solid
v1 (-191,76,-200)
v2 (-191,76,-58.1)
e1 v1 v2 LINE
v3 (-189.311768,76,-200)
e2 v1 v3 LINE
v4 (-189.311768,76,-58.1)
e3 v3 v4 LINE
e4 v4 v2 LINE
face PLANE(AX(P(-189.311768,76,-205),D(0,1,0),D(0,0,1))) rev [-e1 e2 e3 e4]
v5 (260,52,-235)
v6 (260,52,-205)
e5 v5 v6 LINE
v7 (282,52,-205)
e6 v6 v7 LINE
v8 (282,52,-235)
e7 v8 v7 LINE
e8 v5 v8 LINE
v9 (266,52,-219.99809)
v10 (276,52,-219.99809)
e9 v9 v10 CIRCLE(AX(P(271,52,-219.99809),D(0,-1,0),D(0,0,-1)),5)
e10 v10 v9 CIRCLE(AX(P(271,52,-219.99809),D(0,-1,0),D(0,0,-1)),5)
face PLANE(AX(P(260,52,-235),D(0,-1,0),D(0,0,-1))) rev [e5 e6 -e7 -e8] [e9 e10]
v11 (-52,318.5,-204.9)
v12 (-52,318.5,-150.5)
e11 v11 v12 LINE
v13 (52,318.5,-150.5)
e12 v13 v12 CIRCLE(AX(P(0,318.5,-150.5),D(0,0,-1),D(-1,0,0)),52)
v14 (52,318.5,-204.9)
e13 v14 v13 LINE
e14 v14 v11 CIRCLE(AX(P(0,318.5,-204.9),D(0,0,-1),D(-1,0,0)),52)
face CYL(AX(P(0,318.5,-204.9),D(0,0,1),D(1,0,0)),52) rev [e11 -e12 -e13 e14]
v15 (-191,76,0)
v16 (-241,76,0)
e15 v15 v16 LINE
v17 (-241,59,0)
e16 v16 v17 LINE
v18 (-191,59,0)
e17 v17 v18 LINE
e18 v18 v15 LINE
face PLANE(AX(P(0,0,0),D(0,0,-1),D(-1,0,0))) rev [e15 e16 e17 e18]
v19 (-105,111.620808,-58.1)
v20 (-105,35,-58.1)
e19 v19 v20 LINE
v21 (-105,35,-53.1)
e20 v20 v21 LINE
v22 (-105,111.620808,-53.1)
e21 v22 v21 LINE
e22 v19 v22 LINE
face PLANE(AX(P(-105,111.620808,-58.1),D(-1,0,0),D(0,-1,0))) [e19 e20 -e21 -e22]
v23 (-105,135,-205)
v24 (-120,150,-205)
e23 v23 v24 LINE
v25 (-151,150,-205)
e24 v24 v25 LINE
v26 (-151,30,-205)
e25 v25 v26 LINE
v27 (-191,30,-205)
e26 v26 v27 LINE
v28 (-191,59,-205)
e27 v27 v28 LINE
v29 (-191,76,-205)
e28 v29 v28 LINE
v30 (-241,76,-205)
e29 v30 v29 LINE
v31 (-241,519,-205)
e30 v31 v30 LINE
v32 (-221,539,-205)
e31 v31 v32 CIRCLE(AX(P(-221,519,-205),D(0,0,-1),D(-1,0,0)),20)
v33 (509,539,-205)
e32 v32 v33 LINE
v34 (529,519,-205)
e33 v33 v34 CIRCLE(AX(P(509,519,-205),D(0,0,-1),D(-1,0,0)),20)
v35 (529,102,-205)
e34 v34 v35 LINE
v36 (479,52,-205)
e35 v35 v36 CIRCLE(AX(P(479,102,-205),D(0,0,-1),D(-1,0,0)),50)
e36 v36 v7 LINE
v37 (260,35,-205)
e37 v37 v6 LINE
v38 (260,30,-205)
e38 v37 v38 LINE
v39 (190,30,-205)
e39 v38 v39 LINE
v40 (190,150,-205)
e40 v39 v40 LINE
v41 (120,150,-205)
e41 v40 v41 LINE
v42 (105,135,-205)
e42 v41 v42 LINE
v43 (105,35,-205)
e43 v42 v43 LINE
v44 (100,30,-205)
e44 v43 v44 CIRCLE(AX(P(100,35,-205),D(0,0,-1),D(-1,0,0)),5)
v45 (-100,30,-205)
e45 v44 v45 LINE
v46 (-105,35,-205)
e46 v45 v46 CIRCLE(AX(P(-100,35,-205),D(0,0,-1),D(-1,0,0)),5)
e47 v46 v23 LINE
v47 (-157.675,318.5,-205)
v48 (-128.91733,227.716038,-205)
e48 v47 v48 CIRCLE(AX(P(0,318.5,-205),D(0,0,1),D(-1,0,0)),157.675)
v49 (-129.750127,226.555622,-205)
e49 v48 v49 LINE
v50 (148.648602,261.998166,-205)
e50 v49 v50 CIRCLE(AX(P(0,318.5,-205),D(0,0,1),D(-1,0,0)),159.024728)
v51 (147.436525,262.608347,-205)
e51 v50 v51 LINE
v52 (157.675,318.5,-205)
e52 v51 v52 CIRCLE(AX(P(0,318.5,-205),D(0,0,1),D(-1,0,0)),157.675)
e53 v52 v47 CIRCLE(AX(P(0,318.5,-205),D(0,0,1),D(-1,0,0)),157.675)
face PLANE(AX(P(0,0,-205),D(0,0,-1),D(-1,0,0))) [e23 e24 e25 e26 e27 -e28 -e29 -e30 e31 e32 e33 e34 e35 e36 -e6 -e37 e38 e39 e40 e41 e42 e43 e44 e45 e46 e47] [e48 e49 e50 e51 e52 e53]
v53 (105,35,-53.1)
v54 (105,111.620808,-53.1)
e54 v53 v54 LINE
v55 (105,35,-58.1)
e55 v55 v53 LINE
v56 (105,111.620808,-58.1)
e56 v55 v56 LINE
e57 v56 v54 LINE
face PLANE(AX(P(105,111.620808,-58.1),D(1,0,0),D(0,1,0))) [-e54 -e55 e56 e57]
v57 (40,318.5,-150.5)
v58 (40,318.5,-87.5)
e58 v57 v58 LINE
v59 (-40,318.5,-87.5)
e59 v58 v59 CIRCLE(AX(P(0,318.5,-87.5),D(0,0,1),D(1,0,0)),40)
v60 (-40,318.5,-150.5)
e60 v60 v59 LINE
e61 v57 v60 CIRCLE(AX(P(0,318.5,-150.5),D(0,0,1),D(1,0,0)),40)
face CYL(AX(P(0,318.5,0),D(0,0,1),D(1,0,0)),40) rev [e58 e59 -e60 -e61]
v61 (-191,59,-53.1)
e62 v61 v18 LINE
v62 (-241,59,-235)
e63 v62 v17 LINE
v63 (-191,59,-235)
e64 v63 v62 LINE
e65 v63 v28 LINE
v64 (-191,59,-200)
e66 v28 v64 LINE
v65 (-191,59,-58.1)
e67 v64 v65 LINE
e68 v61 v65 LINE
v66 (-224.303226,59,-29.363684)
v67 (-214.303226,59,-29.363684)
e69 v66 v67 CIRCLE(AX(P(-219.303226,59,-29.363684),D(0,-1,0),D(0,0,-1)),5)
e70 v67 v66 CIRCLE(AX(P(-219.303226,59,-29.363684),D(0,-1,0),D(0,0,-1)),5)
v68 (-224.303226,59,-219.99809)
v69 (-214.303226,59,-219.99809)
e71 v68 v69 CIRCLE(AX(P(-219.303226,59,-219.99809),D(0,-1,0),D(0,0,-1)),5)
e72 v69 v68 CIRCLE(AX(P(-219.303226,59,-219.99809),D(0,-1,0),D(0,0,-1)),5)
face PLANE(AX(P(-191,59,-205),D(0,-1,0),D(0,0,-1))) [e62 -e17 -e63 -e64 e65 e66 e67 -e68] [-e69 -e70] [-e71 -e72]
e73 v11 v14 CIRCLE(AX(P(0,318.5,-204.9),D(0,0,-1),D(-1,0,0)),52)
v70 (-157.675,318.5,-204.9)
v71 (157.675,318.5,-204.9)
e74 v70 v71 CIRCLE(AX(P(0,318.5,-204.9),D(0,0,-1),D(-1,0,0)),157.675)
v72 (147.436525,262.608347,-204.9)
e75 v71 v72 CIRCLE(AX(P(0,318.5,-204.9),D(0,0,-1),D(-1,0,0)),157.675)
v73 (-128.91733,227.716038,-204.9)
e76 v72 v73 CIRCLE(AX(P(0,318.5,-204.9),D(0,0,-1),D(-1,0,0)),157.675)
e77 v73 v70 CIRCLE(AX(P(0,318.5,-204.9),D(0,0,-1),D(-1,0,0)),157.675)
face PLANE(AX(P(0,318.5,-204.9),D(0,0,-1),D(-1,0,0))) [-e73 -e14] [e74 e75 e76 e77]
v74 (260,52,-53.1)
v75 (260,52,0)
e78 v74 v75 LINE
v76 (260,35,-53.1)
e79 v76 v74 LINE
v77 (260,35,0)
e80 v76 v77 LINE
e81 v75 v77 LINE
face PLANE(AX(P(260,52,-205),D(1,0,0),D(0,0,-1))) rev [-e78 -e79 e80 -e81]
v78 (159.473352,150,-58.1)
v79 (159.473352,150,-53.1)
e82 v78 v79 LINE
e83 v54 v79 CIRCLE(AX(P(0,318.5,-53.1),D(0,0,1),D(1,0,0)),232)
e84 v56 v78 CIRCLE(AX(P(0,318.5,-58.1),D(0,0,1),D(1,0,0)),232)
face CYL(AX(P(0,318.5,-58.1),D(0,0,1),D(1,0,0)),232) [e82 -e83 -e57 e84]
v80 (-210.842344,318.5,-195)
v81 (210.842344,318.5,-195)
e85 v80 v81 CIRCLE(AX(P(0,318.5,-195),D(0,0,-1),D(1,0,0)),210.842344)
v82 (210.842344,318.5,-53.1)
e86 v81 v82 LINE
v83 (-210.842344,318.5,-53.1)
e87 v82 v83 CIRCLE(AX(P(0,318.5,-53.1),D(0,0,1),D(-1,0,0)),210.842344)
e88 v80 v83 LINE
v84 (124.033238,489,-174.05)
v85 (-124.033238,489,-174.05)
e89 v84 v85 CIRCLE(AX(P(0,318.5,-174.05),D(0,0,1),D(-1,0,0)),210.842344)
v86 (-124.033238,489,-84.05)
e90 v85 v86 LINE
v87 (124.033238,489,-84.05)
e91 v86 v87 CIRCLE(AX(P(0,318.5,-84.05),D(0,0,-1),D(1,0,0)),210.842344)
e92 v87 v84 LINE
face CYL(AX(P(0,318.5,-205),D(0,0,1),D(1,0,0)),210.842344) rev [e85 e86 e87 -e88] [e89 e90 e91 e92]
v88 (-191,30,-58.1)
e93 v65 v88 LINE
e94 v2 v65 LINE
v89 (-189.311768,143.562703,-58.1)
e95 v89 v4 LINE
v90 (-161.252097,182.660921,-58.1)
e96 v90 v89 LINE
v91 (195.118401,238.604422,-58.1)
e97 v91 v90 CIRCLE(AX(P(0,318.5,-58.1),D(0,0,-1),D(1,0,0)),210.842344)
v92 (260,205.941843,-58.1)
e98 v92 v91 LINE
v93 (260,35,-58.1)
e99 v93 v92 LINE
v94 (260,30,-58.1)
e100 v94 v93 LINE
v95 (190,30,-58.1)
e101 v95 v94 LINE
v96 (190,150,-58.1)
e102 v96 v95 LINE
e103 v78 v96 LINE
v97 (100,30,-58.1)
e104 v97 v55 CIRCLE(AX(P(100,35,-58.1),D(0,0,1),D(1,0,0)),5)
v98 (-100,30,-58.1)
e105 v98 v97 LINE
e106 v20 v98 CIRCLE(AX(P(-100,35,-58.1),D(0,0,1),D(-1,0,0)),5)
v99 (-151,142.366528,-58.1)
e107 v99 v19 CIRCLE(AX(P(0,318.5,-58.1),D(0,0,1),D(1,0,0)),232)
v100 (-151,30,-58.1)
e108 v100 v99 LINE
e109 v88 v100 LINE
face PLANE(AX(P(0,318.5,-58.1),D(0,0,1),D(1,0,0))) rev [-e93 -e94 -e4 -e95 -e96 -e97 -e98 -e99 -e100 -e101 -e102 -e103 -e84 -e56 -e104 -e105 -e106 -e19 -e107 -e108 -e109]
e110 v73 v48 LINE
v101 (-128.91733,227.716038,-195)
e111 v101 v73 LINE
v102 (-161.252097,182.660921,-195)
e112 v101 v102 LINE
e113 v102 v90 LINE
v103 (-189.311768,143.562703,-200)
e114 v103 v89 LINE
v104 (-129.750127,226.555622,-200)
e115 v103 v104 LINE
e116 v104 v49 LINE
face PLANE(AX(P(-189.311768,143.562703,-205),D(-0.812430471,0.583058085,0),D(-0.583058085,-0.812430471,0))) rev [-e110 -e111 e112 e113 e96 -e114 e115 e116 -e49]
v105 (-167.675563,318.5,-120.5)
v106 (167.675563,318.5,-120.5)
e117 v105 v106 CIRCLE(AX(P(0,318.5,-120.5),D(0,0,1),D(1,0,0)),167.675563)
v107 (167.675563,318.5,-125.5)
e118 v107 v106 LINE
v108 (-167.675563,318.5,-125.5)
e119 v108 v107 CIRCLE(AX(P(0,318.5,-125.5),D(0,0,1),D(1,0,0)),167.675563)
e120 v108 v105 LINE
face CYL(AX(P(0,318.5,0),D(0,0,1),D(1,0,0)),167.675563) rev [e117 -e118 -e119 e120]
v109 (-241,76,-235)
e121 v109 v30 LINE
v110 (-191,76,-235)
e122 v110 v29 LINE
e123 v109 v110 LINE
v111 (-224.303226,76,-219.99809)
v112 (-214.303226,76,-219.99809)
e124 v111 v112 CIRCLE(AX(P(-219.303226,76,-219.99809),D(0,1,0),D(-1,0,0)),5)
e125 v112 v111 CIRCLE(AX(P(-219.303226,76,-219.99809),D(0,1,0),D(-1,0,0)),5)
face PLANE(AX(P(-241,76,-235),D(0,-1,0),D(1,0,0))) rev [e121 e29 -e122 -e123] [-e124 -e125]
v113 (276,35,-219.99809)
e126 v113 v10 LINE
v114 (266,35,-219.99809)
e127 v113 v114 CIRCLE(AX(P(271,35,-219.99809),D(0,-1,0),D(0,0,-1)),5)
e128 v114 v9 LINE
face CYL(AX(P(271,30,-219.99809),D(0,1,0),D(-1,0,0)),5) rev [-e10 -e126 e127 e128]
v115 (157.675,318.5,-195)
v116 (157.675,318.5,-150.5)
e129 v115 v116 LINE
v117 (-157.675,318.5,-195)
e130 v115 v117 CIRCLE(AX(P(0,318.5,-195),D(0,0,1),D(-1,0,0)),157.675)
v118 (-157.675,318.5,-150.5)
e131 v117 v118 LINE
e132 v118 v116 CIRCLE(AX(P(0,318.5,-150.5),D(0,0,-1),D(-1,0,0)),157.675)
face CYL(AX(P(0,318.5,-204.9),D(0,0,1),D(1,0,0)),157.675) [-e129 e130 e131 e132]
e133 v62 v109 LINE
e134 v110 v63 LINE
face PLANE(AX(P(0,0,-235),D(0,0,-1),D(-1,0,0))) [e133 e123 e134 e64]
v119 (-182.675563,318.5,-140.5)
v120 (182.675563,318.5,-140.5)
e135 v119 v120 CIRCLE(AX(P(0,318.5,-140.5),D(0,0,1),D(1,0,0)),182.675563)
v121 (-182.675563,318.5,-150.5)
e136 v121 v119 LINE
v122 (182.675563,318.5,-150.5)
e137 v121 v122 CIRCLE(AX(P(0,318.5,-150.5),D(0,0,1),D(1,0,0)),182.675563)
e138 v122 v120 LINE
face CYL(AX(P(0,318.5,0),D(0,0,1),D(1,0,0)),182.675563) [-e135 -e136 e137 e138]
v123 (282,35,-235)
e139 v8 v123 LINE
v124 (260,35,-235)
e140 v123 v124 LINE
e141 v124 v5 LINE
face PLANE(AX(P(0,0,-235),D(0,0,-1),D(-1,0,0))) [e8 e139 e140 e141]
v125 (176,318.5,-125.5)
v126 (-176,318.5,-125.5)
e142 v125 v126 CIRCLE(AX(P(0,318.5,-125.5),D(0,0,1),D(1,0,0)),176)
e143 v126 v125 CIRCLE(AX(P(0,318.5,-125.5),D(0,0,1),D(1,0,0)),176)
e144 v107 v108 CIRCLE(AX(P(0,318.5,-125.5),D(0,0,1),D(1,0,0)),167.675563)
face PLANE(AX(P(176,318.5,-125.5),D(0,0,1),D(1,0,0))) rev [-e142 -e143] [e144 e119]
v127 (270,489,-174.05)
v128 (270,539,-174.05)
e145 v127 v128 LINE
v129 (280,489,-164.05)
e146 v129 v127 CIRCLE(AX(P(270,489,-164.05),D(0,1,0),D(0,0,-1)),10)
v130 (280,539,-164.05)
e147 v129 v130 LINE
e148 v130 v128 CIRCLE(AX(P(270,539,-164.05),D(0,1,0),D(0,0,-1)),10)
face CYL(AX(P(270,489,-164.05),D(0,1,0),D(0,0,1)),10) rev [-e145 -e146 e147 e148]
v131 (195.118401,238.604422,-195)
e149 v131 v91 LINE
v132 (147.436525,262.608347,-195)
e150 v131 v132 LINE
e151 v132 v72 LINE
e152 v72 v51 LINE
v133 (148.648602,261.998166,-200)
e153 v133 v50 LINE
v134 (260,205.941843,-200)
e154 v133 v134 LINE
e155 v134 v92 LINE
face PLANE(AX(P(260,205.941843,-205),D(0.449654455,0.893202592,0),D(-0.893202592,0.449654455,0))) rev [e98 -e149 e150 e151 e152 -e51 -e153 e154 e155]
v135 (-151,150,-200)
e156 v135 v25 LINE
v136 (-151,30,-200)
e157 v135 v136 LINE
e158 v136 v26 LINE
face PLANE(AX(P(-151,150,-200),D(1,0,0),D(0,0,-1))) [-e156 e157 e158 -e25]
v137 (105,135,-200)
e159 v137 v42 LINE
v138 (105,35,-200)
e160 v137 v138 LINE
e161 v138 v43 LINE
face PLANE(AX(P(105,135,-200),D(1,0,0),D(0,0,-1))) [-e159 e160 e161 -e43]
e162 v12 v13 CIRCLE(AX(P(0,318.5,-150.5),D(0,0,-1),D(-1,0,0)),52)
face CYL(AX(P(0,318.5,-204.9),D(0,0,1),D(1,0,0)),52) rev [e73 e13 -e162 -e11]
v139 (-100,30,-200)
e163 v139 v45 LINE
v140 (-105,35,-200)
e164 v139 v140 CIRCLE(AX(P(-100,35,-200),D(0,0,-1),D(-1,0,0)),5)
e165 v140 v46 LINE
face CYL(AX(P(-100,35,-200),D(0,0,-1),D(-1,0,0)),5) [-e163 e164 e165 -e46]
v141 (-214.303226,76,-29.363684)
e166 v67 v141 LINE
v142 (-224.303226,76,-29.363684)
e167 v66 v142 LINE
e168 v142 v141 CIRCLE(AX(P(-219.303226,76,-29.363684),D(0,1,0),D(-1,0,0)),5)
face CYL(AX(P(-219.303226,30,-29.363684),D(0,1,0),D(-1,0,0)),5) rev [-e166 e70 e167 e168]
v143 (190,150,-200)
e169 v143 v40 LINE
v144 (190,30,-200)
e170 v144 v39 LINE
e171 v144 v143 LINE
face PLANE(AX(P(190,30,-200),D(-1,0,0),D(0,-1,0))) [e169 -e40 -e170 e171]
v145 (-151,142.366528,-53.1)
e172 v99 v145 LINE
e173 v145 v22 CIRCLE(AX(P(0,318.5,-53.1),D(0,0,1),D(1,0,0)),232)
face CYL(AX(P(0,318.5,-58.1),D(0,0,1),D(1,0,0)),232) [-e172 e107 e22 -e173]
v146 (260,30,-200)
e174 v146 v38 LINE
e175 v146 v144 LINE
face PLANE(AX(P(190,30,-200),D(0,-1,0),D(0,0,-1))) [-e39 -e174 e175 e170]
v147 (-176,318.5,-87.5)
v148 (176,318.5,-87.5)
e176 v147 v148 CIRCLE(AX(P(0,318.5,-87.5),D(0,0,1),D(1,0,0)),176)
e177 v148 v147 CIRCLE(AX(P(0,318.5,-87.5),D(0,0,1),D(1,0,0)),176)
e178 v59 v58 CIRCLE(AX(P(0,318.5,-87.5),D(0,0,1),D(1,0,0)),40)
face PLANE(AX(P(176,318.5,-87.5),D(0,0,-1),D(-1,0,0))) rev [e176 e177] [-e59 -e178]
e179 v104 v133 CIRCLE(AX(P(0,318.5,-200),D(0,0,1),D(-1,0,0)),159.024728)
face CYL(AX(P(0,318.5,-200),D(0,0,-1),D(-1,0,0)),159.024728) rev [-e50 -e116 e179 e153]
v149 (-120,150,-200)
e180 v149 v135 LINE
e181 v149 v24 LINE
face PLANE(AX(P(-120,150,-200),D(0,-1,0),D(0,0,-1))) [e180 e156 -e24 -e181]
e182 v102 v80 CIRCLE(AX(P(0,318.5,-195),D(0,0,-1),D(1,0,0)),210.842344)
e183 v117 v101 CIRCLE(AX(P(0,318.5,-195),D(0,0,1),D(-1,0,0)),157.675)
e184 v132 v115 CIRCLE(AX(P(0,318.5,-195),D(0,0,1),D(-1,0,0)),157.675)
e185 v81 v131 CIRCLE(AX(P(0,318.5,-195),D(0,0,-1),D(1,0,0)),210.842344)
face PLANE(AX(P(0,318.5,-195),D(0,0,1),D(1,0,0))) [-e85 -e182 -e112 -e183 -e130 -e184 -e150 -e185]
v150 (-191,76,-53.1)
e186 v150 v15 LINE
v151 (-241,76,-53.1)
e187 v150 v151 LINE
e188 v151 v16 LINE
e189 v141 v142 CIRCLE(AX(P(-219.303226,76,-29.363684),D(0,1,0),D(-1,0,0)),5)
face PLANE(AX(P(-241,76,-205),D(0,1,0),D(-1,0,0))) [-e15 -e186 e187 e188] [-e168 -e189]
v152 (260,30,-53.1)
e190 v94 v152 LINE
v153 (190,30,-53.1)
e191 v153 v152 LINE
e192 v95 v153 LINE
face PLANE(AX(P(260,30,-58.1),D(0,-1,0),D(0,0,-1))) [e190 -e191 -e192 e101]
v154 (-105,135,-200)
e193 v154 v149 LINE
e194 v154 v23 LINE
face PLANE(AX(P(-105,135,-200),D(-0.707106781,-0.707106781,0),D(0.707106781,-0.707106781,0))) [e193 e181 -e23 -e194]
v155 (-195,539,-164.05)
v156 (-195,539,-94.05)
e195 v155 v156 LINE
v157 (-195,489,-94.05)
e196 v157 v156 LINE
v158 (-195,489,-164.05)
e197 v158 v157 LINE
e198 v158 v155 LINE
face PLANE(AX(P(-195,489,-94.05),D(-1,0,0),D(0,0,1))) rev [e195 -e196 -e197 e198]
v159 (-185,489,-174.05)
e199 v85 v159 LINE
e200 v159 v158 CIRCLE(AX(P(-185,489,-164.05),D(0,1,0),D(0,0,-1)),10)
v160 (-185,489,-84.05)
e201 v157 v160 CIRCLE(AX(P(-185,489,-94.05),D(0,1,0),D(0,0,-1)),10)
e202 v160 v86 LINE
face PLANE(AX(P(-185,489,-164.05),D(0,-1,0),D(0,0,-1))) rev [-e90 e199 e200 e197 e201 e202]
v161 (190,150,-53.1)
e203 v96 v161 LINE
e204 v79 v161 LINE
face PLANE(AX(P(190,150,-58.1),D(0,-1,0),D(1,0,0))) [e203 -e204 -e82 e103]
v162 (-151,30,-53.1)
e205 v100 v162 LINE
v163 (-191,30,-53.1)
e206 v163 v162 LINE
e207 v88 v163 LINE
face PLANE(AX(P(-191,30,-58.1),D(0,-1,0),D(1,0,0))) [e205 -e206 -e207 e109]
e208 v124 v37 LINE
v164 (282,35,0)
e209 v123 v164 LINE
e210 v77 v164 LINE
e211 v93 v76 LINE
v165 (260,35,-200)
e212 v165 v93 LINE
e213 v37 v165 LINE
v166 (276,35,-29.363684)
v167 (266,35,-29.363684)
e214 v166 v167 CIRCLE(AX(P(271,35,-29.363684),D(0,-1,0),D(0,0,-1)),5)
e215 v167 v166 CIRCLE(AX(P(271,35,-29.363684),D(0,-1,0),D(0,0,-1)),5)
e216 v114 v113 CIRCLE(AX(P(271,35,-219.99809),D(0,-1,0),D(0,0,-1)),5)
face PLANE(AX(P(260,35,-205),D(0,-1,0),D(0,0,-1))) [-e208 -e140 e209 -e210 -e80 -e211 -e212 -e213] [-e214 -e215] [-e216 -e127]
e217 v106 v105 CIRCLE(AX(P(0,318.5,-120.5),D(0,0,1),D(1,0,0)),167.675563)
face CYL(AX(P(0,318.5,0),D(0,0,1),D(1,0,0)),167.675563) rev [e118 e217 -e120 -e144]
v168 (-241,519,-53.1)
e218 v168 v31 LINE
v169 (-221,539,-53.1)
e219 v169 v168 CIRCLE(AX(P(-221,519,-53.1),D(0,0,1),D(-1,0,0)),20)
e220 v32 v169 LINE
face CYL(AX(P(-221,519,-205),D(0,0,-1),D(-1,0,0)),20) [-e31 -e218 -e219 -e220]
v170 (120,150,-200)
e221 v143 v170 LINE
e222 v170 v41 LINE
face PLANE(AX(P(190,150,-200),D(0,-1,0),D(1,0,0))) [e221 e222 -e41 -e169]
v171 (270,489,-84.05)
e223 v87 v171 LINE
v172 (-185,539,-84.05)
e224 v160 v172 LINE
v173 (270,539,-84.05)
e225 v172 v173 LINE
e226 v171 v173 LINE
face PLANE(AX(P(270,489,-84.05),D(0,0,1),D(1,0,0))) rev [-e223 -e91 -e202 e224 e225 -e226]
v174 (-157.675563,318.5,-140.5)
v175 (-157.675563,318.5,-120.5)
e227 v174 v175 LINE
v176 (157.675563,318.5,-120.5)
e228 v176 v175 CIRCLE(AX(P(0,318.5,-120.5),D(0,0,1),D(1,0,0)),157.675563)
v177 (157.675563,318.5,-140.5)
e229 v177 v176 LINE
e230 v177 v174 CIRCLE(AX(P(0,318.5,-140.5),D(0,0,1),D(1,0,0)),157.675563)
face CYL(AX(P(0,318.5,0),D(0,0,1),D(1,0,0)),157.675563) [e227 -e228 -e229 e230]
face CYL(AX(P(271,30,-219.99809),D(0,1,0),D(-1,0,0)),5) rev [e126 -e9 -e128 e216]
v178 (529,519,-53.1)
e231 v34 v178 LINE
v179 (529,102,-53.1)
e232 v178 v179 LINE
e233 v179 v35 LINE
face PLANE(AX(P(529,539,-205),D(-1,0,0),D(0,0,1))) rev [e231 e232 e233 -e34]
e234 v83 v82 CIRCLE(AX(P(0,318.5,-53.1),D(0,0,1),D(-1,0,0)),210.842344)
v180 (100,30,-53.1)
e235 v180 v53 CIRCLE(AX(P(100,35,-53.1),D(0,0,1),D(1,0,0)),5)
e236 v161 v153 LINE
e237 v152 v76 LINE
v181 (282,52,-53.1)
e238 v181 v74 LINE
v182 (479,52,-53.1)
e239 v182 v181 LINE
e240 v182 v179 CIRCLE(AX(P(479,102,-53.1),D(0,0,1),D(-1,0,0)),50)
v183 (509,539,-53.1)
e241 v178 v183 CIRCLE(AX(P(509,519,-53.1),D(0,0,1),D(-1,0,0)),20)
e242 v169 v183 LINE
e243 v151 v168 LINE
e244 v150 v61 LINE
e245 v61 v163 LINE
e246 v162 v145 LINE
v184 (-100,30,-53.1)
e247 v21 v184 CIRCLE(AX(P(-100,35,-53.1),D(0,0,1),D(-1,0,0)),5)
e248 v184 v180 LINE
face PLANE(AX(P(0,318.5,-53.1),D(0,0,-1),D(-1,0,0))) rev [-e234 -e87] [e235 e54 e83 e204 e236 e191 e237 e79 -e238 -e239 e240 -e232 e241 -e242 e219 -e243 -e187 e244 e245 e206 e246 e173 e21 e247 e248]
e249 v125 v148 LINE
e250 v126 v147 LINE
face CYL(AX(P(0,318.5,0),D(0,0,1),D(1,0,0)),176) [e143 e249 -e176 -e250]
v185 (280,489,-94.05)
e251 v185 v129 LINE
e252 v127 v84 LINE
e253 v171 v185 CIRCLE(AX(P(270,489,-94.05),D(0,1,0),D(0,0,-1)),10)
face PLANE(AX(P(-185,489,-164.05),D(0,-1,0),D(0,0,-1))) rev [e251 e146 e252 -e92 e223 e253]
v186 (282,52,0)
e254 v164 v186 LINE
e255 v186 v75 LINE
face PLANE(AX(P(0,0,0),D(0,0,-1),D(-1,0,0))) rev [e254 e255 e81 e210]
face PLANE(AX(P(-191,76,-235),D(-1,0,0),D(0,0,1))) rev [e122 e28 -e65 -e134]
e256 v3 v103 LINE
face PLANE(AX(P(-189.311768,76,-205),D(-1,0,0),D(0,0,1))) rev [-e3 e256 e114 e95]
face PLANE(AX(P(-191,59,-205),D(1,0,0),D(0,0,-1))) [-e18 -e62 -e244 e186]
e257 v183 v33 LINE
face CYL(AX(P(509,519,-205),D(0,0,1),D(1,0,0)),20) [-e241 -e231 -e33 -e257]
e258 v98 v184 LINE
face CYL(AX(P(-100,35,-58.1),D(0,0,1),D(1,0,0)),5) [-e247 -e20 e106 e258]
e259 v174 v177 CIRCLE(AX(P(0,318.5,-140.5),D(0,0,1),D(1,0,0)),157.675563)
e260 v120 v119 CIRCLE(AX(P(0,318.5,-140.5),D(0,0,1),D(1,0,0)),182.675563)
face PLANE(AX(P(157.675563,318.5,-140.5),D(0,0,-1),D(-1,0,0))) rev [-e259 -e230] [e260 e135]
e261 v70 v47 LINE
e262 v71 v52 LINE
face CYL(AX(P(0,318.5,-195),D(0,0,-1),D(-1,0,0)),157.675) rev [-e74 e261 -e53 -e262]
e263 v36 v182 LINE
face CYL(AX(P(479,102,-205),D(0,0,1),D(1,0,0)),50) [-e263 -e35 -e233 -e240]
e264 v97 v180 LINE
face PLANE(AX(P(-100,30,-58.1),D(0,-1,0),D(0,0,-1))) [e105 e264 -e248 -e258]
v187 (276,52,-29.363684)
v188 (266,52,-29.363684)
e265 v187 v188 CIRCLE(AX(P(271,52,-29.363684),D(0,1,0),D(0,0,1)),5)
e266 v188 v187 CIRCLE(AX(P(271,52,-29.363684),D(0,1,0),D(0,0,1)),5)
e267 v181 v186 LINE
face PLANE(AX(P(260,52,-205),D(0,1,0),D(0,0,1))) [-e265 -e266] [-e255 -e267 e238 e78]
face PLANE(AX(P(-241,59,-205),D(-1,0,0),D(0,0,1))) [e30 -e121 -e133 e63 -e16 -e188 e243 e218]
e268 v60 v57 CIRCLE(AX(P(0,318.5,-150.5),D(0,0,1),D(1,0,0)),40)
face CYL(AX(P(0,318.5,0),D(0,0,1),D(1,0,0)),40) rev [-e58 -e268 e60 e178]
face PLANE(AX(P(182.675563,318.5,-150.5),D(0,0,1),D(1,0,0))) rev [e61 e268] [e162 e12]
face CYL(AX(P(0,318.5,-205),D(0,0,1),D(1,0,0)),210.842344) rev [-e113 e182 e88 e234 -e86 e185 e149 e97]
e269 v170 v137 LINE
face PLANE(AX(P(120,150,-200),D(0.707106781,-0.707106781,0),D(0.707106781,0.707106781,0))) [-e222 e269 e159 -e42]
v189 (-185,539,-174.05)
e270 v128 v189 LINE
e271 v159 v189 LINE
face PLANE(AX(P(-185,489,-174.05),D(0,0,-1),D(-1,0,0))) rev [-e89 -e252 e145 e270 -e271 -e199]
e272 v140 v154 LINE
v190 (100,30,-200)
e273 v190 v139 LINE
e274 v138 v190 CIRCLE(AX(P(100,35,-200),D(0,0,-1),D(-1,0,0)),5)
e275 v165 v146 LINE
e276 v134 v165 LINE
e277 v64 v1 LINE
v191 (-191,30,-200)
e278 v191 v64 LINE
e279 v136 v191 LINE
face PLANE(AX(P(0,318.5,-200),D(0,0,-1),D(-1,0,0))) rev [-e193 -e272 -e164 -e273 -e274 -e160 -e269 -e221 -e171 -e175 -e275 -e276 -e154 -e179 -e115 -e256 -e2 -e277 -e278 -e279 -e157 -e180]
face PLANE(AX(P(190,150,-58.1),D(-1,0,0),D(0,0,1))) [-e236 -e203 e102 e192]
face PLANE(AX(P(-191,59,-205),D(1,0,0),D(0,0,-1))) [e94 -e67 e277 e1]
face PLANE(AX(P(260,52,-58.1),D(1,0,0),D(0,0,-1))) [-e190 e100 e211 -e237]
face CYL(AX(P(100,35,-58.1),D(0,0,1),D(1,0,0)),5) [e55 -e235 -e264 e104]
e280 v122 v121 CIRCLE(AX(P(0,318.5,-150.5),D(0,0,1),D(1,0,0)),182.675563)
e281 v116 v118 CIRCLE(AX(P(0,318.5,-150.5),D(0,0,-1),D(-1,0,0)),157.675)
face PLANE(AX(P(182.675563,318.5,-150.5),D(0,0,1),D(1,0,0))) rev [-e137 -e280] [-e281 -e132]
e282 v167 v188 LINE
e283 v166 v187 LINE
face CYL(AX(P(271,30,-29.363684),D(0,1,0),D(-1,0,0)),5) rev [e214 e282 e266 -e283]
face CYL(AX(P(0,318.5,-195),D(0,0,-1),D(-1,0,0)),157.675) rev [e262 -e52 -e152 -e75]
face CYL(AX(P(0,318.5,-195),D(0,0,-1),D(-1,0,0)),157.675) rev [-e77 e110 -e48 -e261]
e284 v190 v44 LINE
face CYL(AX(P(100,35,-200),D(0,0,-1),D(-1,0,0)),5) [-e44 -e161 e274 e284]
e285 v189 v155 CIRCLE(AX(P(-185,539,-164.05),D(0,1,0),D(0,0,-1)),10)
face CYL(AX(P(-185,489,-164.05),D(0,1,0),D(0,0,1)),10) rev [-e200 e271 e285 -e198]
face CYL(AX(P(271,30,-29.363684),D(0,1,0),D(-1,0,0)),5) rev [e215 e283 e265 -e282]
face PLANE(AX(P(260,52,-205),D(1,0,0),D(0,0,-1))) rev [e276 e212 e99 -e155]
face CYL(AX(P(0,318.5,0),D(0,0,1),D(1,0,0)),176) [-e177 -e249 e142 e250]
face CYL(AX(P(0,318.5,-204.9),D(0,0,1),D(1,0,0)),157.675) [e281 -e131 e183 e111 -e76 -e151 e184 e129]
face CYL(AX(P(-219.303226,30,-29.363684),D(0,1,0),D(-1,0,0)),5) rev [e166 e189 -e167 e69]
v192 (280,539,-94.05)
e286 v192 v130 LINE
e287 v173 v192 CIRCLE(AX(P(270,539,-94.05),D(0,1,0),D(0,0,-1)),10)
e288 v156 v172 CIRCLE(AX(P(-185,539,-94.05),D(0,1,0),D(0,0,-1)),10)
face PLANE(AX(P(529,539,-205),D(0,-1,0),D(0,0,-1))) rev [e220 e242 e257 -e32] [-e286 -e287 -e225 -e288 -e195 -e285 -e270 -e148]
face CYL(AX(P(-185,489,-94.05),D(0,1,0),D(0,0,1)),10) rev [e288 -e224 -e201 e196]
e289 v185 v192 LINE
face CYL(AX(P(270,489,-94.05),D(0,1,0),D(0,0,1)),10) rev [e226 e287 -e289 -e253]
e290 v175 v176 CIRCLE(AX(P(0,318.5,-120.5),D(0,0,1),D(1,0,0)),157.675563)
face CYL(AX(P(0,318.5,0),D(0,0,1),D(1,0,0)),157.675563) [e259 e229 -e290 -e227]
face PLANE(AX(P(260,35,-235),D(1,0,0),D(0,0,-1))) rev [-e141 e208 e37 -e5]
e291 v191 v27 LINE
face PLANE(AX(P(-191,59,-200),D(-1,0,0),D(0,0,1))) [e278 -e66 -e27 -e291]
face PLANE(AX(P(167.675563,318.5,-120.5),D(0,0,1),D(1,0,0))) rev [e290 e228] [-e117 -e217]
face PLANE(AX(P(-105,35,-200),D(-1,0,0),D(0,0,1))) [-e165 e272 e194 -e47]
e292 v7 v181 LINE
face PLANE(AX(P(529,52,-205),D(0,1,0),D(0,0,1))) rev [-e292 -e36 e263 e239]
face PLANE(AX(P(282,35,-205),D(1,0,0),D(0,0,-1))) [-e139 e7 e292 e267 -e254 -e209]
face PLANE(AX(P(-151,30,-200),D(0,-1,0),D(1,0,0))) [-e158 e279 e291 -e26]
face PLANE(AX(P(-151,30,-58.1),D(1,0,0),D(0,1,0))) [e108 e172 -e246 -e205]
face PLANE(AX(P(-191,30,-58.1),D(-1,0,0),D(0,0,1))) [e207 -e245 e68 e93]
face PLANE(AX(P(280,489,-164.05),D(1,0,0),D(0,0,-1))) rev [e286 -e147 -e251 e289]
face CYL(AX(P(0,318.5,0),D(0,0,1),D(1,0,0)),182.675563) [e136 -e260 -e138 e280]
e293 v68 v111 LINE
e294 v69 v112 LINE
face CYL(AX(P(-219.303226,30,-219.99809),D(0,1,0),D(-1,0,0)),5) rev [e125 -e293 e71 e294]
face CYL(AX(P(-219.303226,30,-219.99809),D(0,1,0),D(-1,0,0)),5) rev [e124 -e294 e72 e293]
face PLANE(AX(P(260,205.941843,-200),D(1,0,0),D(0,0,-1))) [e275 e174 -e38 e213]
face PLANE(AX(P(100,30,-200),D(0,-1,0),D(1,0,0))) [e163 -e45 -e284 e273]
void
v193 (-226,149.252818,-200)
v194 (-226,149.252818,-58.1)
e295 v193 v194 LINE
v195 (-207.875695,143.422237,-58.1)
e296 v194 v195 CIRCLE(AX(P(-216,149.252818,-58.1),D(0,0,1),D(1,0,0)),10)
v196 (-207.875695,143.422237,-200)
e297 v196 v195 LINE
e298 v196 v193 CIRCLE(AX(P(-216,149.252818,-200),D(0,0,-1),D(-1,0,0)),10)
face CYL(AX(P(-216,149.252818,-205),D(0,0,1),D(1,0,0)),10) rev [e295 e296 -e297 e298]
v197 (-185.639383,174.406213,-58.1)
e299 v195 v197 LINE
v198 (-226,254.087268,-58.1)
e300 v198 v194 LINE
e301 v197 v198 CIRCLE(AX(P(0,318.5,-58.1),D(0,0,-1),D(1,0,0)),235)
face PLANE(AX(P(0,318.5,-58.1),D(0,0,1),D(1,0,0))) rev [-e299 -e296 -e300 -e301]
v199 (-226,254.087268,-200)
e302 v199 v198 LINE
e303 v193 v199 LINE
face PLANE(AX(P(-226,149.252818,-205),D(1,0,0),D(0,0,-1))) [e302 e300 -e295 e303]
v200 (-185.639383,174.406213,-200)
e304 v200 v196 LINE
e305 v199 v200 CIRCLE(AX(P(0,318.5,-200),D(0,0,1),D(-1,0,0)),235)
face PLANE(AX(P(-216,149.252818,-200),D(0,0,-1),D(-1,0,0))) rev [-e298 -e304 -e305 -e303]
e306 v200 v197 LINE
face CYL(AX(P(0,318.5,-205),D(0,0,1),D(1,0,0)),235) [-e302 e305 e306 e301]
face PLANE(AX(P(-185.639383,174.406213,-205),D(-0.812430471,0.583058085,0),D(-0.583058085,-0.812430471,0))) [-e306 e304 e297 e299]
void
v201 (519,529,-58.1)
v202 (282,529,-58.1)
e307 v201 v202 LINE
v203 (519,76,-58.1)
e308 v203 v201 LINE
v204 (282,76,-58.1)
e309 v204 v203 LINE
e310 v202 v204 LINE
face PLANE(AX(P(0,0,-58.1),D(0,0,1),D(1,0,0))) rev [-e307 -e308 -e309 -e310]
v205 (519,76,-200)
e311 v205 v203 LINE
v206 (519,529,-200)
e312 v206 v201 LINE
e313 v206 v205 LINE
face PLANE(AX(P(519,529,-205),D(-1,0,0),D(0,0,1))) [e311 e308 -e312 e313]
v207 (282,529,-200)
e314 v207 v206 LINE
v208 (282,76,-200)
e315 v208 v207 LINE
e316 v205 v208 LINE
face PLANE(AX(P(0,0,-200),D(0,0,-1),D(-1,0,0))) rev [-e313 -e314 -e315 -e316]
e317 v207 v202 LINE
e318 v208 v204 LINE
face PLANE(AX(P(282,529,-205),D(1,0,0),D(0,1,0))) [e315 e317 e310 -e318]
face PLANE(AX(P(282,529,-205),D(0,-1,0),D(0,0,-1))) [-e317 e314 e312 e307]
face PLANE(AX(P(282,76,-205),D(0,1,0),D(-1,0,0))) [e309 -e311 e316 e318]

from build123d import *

# Parameters (mm, degrees)
SKETCH2_W             = 50
SKETCH2_H             = 17
BOSS_EXTRUDE1_DEPTH   = 205
SKETCH2_W_2           = 22
BOSS_EXTRUDE1_2_DEPTH = 205
SKETCH3_W             = 237
SKETCH3_H             = 453
BOSS_EXTRUDE2_DEPTH   = 151.9
BOSS_EXTRUDE3_DEPTH   = 10
SKETCH5_W             = 237
SKETCH5_H             = 453
BOSS_EXTRUDE4_DEPTH   = 5
SKETCH6_W             = 237
SKETCH6_H             = 453
BOSS_EXTRUDE5_DEPTH   = 5
BOSS_EXTRUDE7_DEPTH   = 5
BOSS_EXTRUDE8_DEPTH   = 5
BOSS_EXTRUDE9_DEPTH   = 5
FILLET1_R             = 20
FILLET2_R             = 50
CUT_EXTRUDE1_DEPTH    = 50
SKETCH13_W            = 50
SKETCH13_H            = 17
SKETCH13_W_2          = 22
BOSS_EXTRUDE10_DEPTH  = 30
SKETCH14_R            = 5
CUT_EXTRUDE2_DEPTH    = 742.238827909
SKETCH16_R            = 157.675
SKETCH16_R_2          = 52
BOSS_EXTRUDE12_DEPTH  = 54.4


with BuildPart() as part:
    # Sketch1 → Revolve1 (revolve)
    with BuildSketch(Plane(origin=(0, 318.5, 0), x_dir=(-1, 0, 0), z_dir=(0, -1, 0))):
        Polygon((-176, 125.5), (-167.675563156, 125.5), (-167.675563156, 120.5), (-157.675563156, 120.5), (-157.675563156, 140.5), (-182.675563156, 140.5), (-182.675563156, 150.5), (-40, 150.5), (-40, 87.5), (-176, 87.5), align=None)
    revolve(axis=Axis((0, 318.5, 0), (0, 0, -1)))



with BuildPart() as body_2:
    # Sketch2 → Boss-Extrude1 (new body)
    with BuildSketch(Plane.XY):
        with Locations((-216, 67.5)):
            Rectangle(SKETCH2_W, SKETCH2_H)
    extrude(amount=-BOSS_EXTRUDE1_DEPTH)



with BuildPart() as body_3:
    # Sketch2 → Boss-Extrude1 2 (new body)
    with BuildSketch(Plane.XY):
        with Locations((271, 43.5)):
            Rectangle(SKETCH2_W_2, SKETCH2_H)
    extrude(amount=-BOSS_EXTRUDE1_2_DEPTH)


with BuildPart() as body_2_1:
    add(body_2.part)

    add(body_3.part)  # Boss-Extrude2 merges body 3
    # Sketch3 → Boss-Extrude2 (add)
    with BuildSketch(Plane(origin=(0, 0, -53.1), x_dir=(-1, 0, 0), z_dir=(0, 0, -1))):
        with BuildLine():
            Line((-529, 539), (241, 539))
            Line((241, 539), (241, 76))
            Line((241, 76), (189.311768485, 76))
            Line((189.311768485, 76), (189.311768485, 143.562703206))
            Line((189.311768485, 143.562703206), (161.252096874, 182.66092141))
            ThreePointArc((161.252096874, 182.66092141), (32.69786622, 526.791487015), (-195.118401486, 238.604421776))
            Line((-195.118401486, 238.604421776), (-260, 205.941843226))
            Line((-260, 205.941843226), (-260, 52))
            Line((-260, 52), (-529, 52))
            Line((-529, 52), (-529, 539))
        make_face()
        with Locations((-400.5, 302.5)):
            Rectangle(SKETCH3_W, SKETCH3_H, mode=Mode.SUBTRACT)
        with BuildLine():
            Line((185.639383115, 174.406213053), (207.875695292, 143.422237275))
            ThreePointArc((207.875695292, 143.422237275), (219.062429829, 139.733284333), (226, 149.252818121))
            Line((226, 149.252818121), (226, 254.087268339))
            ThreePointArc((226, 254.087268339), (209.640199093, 212.311549949), (185.639383115, 174.406213053))
        make_face(mode=Mode.SUBTRACT)
    extrude(amount=BOSS_EXTRUDE2_DEPTH)

    # Sketch4 → Boss-Extrude3 (add)
    with BuildSketch(Plane(origin=(0, 0, -205), x_dir=(-1, 0, 0), z_dir=(0, 0, -1))):
        with BuildLine():
            Line((-196.910166335, 237.702414713), (-147.436524546, 262.608347182))
            ThreePointArc((-147.436524546, 262.608347182), (19.751163276, 474.933043742), (128.917329729, 227.716038197))
            Line((128.917329729, 227.716038197), (162.454726893, 180.985182237))
            ThreePointArc((162.454726893, 180.985182237), (33.181402046, 528.740000839), (-196.910166335, 237.702414713))
        make_face()
    extrude(amount=-BOSS_EXTRUDE3_DEPTH)

    # Sketch5 → Boss-Extrude4 (add)
    with BuildSketch(Plane(origin=(0, 0, -205), x_dir=(-1, 0, 0), z_dir=(0, 0, -1))):
        with Locations((-400.5, 302.5)):
            Rectangle(SKETCH5_W, SKETCH5_H)
    extrude(amount=-BOSS_EXTRUDE4_DEPTH)

    # Sketch6 → Boss-Extrude5 (add)
    with BuildSketch(Plane.XY.offset(-53.1)):
        with Locations((400.5, 302.5)):
            Rectangle(SKETCH6_W, SKETCH6_H)
    extrude(amount=-BOSS_EXTRUDE5_DEPTH)

    # Sketch8 → Boss-Extrude7 (add)
    with BuildSketch(Plane(origin=(0, 0, -205), x_dir=(-1, 0, 0), z_dir=(0, 0, -1))):
        with BuildLine():
            Line((-190, 30), (-190, 150))
            Line((-190, 150), (-120, 150))
            Line((-120, 150), (-105, 135))
            Line((-105, 135), (-105, 35))
            ThreePointArc((-105, 35), (-103.535533906, 31.464466094), (-100, 30))
            Line((-100, 30), (100, 30))
            ThreePointArc((100, 30), (103.535533906, 31.464466094), (105, 35))
            Line((105, 35), (105, 135))
            Line((105, 135), (120, 150))
            Line((120, 150), (151, 150))
            Line((151, 150), (151, 30))
            Line((151, 30), (191, 30))
            Line((191, 30), (191, 59))
            Line((191, 59), (191, 76))
            Line((191, 76), (189.311768485, 76))
            Line((189.311768485, 76), (189.311768485, 143.562703206))
            Line((189.311768485, 143.562703206), (129.750126988, 226.555622302))
            ThreePointArc((129.750126988, 226.555622302), (-20.083116117, 160.748510338), (-148.64860156, 261.998165534))
            Line((-148.64860156, 261.998165534), (-260, 205.941843226))
            Line((-260, 205.941843226), (-260, 30))
            Line((-260, 30), (-190, 30))
        make_face()
    extrude(amount=-BOSS_EXTRUDE7_DEPTH)

    # Sketch9 → Boss-Extrude8 (add)
    with BuildSketch(Plane.XY.offset(-53.1)):
        with BuildLine():
            Line((-185.639383115, 174.406213053), (-207.875695292, 143.422237275))
            ThreePointArc((-207.875695292, 143.422237275), (-219.062429829, 139.733284333), (-226, 149.252818121))
            Line((-226, 149.252818121), (-226, 254.087268339))
            ThreePointArc((-226, 254.087268339), (-209.640199093, 212.311549949), (-185.639383115, 174.406213053))
        make_face()
        with BuildLine():
            Line((-189.311768485, 143.562703206), (-189.311768485, 76))
            Line((-189.311768485, 76), (-191, 76))
            Line((-191, 76), (-191, 30))
            Line((-191, 30), (-151, 30))
            Line((-151, 30), (-151, 142.366527883))
            ThreePointArc((-151, 142.366527883), (-128.919838736, 125.617457554), (-105, 111.6208082))
            Line((-105, 111.6208082), (-105, 35))
            ThreePointArc((-105, 35), (-103.535533906, 31.464466094), (-100, 30))
            Line((-100, 30), (100, 30))
            ThreePointArc((100, 30), (103.535533906, 31.464466094), (105, 35))
            Line((105, 35), (105, 111.6208082))
            ThreePointArc((105, 111.6208082), (133.621776186, 128.844467708), (159.473352006, 150))
            Line((159.473352006, 150), (190, 150))
            Line((190, 150), (190, 30))
            Line((190, 30), (260, 30))
            Line((260, 30), (260, 35))
            Line((260, 35), (260, 52))
            Line((260, 52), (260, 205.941843226))
            Line((260, 205.941843226), (195.118401486, 238.604421776))
            ThreePointArc((195.118401486, 238.604421776), (32.69786622, 110.208512985), (-161.252096874, 182.66092141))
            Line((-161.252096874, 182.66092141), (-189.311768485, 143.562703206))
        make_face()
    extrude(amount=-BOSS_EXTRUDE8_DEPTH)

    # Sketch10 → Boss-Extrude9 (add)
    with BuildSketch(Plane(origin=(0, 0, -205), x_dir=(-1, 0, 0), z_dir=(0, 0, -1))):
        with BuildLine():
            Line((226, 149.252818121), (226, 254.087268339))
            ThreePointArc((226, 254.087268339), (209.640199093, 212.311549949), (185.639383115, 174.406213053))
            Line((185.639383115, 174.406213053), (207.875695292, 143.422237275))
            ThreePointArc((207.875695292, 143.422237275), (219.062429829, 139.733284333), (226, 149.252818121))
        make_face()
    extrude(amount=-BOSS_EXTRUDE9_DEPTH)

    # Fillet1
    fillet1_edges = [body_2_1.edges().sort_by_distance(p)[0] for p in [
        (-241, 539, -129.05),
        (529, 539, -129.05),
    ]]
    fillet(fillet1_edges, radius=FILLET1_R)

    # Fillet2
    fillet2_edges = [body_2_1.edges().sort_by_distance(p)[0] for p in [
        (529, 52, -129.05),
    ]]
    fillet(fillet2_edges, radius=FILLET2_R)

    # Sketch12 → Cut-Extrude1 (cut)
    with BuildSketch(Plane(origin=(0, 539, 0), x_dir=(1, 0, 0), z_dir=(0, 1, 0))):
        with BuildLine():
            Line((-185, 174.05), (270, 174.05))
            ThreePointArc((270, 174.05), (277.071067812, 171.121067812), (280, 164.05))
            Line((280, 164.05), (280, 94.05))
            ThreePointArc((280, 94.05), (277.071067812, 86.978932188), (270, 84.05))
            Line((270, 84.05), (-185, 84.05))
            ThreePointArc((-185, 84.05), (-192.071067812, 86.978932188), (-195, 94.05))
            Line((-195, 94.05), (-195, 164.05))
            ThreePointArc((-195, 164.05), (-192.071067812, 171.121067812), (-185, 174.05))
        make_face()
    extrude(amount=-CUT_EXTRUDE1_DEPTH, mode=Mode.SUBTRACT)

    # Sketch13 → Boss-Extrude10 (add)
    with BuildSketch(Plane(origin=(0, 0, -205), x_dir=(-1, 0, 0), z_dir=(0, 0, -1))):
        with Locations((216, 67.5)):
            Rectangle(SKETCH13_W, SKETCH13_H)
        with Locations((-271, 43.5)):
            Rectangle(SKETCH13_W_2, SKETCH13_H)
    extrude(amount=BOSS_EXTRUDE10_DEPTH)

    # Sketch14 → Cut-Extrude2 (cut, through all)
    with BuildSketch(Plane(origin=(0, 76, 0), x_dir=(1, 0, 0), z_dir=(0, 1, 0))):
        with Locations(Location((-219.303225542, 219.998090208, 0), (0, 0, 180))):
            Circle(SKETCH14_R)
        with Locations(Location((-219.303225542, 29.3636836, 0), (0, 0, 180))):
            Circle(SKETCH14_R)
        with Locations(Location((271, 219.998090208, 0), (0, 0, 90))):
            Circle(SKETCH14_R)
        with Locations(Location((271, 29.3636836, 0), (0, 0, 180))):
            Circle(SKETCH14_R)
    extrude(amount=-CUT_EXTRUDE2_DEPTH, mode=Mode.SUBTRACT)


with BuildPart() as part_1:
    add(part.part)

    add(body_2_1.part)  # Boss-Extrude12 merges body 2
    # Sketch16 → Boss-Extrude12 (add)
    with BuildSketch(Plane(origin=(0, 0, -150.5), x_dir=(-1, 0, 0), z_dir=(0, 0, -1))):
        with Locations(Location((0, 318.5, 0), (0, 0, 200.761196854))):
            Circle(SKETCH16_R)
        with Locations((0, 318.5)):
            Circle(SKETCH16_R_2, mode=Mode.SUBTRACT)
    extrude(amount=BOSS_EXTRUDE12_DEPTH)


solid = part_1.part
